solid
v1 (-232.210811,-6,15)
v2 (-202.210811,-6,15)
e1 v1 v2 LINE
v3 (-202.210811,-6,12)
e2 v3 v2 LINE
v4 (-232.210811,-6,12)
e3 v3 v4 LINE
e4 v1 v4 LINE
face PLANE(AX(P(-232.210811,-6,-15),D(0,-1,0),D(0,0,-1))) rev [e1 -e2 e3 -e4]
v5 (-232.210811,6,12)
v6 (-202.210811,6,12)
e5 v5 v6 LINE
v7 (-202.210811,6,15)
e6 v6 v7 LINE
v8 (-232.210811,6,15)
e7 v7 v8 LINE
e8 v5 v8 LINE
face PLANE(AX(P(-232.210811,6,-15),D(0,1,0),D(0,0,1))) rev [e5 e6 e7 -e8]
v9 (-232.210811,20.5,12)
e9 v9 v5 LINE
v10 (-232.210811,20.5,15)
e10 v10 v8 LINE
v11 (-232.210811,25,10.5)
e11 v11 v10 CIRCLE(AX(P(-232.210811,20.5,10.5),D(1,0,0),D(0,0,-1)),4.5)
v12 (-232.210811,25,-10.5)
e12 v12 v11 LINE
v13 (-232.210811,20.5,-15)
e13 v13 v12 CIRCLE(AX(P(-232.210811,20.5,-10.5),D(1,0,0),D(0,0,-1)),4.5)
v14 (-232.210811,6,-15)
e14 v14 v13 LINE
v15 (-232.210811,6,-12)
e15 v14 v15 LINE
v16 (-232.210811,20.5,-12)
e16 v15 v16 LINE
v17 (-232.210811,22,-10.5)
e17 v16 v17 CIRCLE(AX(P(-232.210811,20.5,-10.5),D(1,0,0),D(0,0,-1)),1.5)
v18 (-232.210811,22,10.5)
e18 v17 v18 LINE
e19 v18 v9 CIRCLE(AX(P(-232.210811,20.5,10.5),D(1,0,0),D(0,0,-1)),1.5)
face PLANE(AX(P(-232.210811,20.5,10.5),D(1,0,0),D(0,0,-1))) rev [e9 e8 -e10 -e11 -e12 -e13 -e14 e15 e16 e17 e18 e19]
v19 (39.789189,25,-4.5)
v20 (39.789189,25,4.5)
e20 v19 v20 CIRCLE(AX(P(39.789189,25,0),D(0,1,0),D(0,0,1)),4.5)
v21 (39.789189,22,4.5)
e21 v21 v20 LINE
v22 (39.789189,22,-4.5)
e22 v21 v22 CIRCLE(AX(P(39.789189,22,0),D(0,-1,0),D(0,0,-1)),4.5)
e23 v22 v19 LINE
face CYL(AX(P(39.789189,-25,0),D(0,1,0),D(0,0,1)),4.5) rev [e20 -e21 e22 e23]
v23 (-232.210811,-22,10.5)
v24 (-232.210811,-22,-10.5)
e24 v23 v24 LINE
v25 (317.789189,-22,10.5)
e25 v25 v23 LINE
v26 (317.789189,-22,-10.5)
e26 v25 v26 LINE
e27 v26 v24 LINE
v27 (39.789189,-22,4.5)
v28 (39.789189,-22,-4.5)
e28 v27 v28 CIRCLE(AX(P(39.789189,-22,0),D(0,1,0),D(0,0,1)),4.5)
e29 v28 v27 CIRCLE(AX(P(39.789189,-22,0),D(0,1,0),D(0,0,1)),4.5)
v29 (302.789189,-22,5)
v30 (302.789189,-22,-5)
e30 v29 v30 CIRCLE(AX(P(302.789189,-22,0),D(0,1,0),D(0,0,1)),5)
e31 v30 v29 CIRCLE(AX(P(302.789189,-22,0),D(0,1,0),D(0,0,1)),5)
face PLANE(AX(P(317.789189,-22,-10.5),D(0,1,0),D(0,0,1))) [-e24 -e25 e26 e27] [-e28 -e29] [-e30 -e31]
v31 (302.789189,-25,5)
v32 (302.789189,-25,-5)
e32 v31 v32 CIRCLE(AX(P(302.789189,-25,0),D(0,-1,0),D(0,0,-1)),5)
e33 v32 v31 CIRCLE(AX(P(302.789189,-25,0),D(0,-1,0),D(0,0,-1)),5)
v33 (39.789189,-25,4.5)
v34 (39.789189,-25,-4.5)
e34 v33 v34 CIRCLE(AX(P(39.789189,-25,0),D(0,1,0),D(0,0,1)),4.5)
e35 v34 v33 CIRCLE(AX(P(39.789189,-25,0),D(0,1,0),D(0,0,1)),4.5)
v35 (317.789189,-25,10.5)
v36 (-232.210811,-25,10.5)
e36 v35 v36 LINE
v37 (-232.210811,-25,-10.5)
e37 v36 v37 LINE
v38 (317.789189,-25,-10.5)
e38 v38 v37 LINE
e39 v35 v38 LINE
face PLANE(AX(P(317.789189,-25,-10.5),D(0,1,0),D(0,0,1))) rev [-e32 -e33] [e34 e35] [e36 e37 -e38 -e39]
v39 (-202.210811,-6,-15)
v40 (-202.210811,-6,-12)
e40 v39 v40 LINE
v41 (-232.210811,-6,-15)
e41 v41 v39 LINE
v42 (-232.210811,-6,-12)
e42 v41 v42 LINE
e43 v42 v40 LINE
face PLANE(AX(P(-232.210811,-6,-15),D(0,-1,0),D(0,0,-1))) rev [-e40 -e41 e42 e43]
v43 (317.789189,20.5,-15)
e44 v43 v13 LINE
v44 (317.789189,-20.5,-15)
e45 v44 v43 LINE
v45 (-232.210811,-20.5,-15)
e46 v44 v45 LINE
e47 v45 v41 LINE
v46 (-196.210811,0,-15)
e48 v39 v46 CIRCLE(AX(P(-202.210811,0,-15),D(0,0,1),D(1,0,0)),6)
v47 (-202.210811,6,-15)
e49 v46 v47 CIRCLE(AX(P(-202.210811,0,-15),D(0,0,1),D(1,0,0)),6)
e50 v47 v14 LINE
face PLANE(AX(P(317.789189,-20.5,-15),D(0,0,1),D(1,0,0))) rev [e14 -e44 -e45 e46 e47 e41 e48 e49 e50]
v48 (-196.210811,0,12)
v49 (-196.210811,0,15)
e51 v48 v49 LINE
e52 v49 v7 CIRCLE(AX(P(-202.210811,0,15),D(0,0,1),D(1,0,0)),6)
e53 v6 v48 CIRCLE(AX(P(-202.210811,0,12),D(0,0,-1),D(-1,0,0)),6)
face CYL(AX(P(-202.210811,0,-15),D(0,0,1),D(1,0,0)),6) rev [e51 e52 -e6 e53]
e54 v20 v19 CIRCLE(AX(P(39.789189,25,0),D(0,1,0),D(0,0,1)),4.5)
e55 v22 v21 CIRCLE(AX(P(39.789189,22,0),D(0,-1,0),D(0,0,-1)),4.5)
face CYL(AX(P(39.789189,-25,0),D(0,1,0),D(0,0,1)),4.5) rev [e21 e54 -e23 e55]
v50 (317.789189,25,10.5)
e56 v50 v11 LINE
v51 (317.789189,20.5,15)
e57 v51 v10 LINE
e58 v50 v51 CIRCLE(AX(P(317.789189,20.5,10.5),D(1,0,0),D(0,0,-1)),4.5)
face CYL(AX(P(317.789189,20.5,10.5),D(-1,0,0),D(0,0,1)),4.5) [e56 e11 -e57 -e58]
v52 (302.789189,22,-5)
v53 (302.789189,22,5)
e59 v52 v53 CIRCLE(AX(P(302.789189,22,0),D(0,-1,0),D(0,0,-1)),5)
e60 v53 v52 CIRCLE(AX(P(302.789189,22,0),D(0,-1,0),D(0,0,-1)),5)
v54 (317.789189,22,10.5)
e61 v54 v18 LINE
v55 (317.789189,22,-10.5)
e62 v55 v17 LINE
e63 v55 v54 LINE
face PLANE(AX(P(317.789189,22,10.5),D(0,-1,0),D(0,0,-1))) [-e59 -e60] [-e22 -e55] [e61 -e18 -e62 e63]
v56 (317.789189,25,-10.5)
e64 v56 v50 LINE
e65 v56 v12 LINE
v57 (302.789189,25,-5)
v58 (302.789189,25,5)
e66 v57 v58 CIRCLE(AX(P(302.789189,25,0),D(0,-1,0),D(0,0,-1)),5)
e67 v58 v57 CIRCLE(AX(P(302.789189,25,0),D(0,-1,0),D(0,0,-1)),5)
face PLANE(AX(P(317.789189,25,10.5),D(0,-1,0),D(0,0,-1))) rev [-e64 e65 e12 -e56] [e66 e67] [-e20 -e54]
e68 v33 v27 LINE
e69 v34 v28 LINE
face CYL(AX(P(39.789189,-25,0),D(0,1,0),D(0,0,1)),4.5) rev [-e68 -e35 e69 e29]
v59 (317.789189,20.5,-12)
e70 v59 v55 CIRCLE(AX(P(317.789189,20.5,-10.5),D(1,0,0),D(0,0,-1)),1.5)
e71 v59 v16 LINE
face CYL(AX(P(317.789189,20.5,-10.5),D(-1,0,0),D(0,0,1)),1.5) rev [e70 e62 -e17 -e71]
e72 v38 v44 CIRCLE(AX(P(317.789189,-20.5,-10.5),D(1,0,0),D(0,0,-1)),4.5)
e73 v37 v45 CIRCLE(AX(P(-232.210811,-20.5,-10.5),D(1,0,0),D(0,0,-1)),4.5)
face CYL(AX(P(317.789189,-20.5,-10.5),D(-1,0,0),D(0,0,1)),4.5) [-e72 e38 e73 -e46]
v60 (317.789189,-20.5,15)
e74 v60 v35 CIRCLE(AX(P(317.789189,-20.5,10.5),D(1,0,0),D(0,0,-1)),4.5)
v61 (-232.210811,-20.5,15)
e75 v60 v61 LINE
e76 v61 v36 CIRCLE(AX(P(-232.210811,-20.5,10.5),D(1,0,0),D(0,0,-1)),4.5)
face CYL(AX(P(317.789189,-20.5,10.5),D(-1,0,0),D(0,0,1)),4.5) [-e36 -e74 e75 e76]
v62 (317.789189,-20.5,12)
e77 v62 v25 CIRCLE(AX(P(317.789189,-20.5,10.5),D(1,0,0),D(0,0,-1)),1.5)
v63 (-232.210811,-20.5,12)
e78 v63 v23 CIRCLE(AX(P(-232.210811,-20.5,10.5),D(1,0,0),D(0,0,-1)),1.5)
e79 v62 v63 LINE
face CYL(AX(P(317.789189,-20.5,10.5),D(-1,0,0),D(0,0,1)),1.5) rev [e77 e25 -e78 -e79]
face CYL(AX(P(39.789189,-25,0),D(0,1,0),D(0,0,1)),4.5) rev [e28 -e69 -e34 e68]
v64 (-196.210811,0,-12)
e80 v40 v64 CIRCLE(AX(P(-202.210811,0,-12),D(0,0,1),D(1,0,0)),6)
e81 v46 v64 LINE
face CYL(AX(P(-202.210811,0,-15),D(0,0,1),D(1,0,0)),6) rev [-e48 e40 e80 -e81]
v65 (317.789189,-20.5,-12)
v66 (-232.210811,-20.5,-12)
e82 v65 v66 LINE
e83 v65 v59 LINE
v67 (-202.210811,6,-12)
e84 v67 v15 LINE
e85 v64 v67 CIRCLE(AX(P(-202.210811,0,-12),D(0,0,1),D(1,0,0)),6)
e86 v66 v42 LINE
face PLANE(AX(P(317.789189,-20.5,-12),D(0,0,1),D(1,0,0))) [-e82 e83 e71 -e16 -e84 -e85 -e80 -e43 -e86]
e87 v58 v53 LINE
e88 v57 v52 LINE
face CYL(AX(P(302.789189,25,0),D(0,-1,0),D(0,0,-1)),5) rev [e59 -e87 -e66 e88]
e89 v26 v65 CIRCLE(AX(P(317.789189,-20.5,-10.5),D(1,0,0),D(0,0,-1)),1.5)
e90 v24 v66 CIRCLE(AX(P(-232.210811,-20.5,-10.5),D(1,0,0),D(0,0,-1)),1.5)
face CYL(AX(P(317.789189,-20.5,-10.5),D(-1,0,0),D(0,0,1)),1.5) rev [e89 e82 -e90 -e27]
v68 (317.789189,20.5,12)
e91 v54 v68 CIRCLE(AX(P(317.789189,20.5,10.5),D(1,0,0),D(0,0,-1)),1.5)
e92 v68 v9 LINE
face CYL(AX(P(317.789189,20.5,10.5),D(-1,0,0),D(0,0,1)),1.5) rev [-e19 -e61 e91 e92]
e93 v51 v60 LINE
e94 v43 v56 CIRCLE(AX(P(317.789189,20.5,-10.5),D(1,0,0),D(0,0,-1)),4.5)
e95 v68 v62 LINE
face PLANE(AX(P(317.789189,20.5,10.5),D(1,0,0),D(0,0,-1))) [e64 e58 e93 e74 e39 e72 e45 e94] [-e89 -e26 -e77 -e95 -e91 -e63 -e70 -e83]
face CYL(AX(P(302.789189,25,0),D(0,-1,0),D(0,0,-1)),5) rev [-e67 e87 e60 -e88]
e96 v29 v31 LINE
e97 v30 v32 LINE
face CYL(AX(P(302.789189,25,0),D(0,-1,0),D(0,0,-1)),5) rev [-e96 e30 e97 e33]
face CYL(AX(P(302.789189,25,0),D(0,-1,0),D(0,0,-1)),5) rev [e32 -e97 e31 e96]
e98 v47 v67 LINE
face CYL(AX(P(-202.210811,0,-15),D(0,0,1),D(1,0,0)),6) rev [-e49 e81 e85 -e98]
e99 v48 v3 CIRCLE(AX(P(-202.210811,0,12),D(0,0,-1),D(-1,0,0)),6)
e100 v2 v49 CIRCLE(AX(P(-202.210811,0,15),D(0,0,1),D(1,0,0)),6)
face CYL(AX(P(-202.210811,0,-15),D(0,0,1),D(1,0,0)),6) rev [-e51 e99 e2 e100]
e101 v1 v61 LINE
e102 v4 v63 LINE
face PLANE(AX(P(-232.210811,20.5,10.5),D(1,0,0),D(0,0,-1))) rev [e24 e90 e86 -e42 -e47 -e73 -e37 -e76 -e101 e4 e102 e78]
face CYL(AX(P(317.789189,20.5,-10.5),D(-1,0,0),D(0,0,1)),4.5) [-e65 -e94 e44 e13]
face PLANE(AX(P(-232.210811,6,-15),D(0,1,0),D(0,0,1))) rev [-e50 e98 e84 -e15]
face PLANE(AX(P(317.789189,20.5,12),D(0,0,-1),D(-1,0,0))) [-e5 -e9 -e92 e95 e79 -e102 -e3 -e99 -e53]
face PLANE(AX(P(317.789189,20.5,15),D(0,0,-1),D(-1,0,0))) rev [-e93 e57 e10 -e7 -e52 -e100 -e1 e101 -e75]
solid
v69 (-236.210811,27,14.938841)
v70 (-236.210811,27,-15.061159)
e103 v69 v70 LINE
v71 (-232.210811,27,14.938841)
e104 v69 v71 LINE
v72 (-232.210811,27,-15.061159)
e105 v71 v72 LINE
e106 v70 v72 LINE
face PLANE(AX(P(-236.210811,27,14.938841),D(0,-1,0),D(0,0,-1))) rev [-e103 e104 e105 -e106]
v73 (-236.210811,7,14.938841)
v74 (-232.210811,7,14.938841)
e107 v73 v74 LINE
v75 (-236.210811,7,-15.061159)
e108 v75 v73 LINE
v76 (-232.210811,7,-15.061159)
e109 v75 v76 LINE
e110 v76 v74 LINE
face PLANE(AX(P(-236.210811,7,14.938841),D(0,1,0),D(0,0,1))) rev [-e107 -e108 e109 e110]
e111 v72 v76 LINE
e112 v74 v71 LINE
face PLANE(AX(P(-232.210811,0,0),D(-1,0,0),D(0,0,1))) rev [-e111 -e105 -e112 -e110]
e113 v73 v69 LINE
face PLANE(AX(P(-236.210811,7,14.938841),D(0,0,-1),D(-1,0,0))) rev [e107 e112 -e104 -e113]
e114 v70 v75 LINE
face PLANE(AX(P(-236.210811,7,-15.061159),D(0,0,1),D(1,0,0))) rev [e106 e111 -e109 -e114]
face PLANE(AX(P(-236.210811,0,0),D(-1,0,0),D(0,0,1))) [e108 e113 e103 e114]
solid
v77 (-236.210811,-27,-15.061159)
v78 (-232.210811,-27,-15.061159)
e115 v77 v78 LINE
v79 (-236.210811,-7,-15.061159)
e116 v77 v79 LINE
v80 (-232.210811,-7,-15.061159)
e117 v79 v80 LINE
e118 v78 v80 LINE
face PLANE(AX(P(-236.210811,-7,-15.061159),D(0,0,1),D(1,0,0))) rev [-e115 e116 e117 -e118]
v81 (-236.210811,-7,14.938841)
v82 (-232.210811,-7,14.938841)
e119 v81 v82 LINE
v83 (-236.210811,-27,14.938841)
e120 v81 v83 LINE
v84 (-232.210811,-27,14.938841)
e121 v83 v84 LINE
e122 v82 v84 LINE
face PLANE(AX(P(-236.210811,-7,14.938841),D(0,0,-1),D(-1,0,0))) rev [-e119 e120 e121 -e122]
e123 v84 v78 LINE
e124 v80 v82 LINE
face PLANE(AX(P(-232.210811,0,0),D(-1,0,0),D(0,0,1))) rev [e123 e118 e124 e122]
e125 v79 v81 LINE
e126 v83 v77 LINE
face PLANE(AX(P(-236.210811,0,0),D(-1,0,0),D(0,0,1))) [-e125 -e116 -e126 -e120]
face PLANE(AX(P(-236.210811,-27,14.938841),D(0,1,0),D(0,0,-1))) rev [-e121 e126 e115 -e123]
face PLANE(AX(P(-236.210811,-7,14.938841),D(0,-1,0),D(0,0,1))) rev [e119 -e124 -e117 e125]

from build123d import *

# Parameters (mm, degrees)
STRUCTURAL_MEMBER2_DEPTH = 550
CUT_EXTRUDE1_DEPTH       = 321.179588302
SKETCH5_R                = 5
CUT_EXTRUDE2_DEPTH       = 50
SKETCH6_R                = 4.5
CUT_EXTRUDE3_DEPTH       = 323.048084555
SKETCH7_W                = 30
SKETCH7_H                = 20
BOSS_EXTRUDE1_DEPTH      = 4


with BuildPart() as part:
    # Sketch1 → Structural Member2 (new body)
    with BuildSketch(Plane.YZ.offset(-232.210810811)):
        with BuildLine():
            Line((-20.5, -15), (20.5, -15))
            ThreePointArc((20.5, -15), (23.681980515, -13.681980515), (25, -10.5))
            Line((25, -10.5), (25, 10.5))
            ThreePointArc((25, 10.5), (23.681980515, 13.681980515), (20.5, 15))
            Line((20.5, 15), (-20.5, 15))
            ThreePointArc((-20.5, 15), (-23.681980515, 13.681980515), (-25, 10.5))
            Line((-25, 10.5), (-25, -10.5))
            ThreePointArc((-25, -10.5), (-23.681980515, -13.681980515), (-20.5, -15))
        make_face()
        with BuildLine():
            Line((-20.5, -12), (20.5, -12))
            ThreePointArc((20.5, -12), (21.560660172, -11.560660172), (22, -10.5))
            Line((22, -10.5), (22, 10.5))
            ThreePointArc((22, 10.5), (21.560660172, 11.560660172), (20.5, 12))
            Line((20.5, 12), (-20.5, 12))
            ThreePointArc((-20.5, 12), (-21.560660172, 11.560660172), (-22, 10.5))
            Line((-22, 10.5), (-22, -10.5))
            ThreePointArc((-22, -10.5), (-21.560660172, -11.560660172), (-20.5, -12))
        make_face(mode=Mode.SUBTRACT)
    extrude(amount=STRUCTURAL_MEMBER2_DEPTH)

    # Sketch4 → Cut-Extrude1 (cut, through all)
    with BuildSketch(Plane.XY.offset(15)):
        with BuildLine():
            Line((-232.210810811, 6), (-202.210810811, 6))
            ThreePointArc((-202.210810811, 6), (-196.210810811, 0), (-202.210810811, -6))
            Line((-202.210810811, -6), (-232.210810811, -6))
            ThreePointArc((-232.210810811, -6), (-238.210810811, 0), (-232.210810811, 6))
        make_face()
    extrude(amount=-CUT_EXTRUDE1_DEPTH, mode=Mode.SUBTRACT)

    # Sketch5 → Cut-Extrude2 (cut)
    with BuildSketch(Plane(origin=(0, -25, 0), x_dir=(-1, 0, 0), z_dir=(0, -1, 0))):
        with Locations(Location((-302.789189189, 0, 0), (0, 0, 90))):
            Circle(SKETCH5_R)
    extrude(amount=-CUT_EXTRUDE2_DEPTH, mode=Mode.SUBTRACT)

    # Sketch6 → Cut-Extrude3 (cut, through all)
    with BuildSketch(Plane(origin=(0, 25, 0), x_dir=(1, 0, 0), z_dir=(0, 1, 0))):
        with Locations(Location((39.789189189, 0, 0), (0, 0, 270))):
            Circle(SKETCH6_R)
    extrude(amount=-CUT_EXTRUDE3_DEPTH, mode=Mode.SUBTRACT)


with BuildPart() as body_2:
    # Sketch7 → Boss-Extrude1 (new body)
    with BuildSketch(Plane.ZY.offset(232.210810811)):
        with Locations((-0.061159419, 17)):
            Rectangle(SKETCH7_W, SKETCH7_H)
    extrude(amount=BOSS_EXTRUDE1_DEPTH)


with BuildPart() as body_3:
    # Mirror2: mirrored copy
    add(body_2.part.mirror(Plane.ZX))


solid = Compound([part.part, body_2.part, body_3.part])
